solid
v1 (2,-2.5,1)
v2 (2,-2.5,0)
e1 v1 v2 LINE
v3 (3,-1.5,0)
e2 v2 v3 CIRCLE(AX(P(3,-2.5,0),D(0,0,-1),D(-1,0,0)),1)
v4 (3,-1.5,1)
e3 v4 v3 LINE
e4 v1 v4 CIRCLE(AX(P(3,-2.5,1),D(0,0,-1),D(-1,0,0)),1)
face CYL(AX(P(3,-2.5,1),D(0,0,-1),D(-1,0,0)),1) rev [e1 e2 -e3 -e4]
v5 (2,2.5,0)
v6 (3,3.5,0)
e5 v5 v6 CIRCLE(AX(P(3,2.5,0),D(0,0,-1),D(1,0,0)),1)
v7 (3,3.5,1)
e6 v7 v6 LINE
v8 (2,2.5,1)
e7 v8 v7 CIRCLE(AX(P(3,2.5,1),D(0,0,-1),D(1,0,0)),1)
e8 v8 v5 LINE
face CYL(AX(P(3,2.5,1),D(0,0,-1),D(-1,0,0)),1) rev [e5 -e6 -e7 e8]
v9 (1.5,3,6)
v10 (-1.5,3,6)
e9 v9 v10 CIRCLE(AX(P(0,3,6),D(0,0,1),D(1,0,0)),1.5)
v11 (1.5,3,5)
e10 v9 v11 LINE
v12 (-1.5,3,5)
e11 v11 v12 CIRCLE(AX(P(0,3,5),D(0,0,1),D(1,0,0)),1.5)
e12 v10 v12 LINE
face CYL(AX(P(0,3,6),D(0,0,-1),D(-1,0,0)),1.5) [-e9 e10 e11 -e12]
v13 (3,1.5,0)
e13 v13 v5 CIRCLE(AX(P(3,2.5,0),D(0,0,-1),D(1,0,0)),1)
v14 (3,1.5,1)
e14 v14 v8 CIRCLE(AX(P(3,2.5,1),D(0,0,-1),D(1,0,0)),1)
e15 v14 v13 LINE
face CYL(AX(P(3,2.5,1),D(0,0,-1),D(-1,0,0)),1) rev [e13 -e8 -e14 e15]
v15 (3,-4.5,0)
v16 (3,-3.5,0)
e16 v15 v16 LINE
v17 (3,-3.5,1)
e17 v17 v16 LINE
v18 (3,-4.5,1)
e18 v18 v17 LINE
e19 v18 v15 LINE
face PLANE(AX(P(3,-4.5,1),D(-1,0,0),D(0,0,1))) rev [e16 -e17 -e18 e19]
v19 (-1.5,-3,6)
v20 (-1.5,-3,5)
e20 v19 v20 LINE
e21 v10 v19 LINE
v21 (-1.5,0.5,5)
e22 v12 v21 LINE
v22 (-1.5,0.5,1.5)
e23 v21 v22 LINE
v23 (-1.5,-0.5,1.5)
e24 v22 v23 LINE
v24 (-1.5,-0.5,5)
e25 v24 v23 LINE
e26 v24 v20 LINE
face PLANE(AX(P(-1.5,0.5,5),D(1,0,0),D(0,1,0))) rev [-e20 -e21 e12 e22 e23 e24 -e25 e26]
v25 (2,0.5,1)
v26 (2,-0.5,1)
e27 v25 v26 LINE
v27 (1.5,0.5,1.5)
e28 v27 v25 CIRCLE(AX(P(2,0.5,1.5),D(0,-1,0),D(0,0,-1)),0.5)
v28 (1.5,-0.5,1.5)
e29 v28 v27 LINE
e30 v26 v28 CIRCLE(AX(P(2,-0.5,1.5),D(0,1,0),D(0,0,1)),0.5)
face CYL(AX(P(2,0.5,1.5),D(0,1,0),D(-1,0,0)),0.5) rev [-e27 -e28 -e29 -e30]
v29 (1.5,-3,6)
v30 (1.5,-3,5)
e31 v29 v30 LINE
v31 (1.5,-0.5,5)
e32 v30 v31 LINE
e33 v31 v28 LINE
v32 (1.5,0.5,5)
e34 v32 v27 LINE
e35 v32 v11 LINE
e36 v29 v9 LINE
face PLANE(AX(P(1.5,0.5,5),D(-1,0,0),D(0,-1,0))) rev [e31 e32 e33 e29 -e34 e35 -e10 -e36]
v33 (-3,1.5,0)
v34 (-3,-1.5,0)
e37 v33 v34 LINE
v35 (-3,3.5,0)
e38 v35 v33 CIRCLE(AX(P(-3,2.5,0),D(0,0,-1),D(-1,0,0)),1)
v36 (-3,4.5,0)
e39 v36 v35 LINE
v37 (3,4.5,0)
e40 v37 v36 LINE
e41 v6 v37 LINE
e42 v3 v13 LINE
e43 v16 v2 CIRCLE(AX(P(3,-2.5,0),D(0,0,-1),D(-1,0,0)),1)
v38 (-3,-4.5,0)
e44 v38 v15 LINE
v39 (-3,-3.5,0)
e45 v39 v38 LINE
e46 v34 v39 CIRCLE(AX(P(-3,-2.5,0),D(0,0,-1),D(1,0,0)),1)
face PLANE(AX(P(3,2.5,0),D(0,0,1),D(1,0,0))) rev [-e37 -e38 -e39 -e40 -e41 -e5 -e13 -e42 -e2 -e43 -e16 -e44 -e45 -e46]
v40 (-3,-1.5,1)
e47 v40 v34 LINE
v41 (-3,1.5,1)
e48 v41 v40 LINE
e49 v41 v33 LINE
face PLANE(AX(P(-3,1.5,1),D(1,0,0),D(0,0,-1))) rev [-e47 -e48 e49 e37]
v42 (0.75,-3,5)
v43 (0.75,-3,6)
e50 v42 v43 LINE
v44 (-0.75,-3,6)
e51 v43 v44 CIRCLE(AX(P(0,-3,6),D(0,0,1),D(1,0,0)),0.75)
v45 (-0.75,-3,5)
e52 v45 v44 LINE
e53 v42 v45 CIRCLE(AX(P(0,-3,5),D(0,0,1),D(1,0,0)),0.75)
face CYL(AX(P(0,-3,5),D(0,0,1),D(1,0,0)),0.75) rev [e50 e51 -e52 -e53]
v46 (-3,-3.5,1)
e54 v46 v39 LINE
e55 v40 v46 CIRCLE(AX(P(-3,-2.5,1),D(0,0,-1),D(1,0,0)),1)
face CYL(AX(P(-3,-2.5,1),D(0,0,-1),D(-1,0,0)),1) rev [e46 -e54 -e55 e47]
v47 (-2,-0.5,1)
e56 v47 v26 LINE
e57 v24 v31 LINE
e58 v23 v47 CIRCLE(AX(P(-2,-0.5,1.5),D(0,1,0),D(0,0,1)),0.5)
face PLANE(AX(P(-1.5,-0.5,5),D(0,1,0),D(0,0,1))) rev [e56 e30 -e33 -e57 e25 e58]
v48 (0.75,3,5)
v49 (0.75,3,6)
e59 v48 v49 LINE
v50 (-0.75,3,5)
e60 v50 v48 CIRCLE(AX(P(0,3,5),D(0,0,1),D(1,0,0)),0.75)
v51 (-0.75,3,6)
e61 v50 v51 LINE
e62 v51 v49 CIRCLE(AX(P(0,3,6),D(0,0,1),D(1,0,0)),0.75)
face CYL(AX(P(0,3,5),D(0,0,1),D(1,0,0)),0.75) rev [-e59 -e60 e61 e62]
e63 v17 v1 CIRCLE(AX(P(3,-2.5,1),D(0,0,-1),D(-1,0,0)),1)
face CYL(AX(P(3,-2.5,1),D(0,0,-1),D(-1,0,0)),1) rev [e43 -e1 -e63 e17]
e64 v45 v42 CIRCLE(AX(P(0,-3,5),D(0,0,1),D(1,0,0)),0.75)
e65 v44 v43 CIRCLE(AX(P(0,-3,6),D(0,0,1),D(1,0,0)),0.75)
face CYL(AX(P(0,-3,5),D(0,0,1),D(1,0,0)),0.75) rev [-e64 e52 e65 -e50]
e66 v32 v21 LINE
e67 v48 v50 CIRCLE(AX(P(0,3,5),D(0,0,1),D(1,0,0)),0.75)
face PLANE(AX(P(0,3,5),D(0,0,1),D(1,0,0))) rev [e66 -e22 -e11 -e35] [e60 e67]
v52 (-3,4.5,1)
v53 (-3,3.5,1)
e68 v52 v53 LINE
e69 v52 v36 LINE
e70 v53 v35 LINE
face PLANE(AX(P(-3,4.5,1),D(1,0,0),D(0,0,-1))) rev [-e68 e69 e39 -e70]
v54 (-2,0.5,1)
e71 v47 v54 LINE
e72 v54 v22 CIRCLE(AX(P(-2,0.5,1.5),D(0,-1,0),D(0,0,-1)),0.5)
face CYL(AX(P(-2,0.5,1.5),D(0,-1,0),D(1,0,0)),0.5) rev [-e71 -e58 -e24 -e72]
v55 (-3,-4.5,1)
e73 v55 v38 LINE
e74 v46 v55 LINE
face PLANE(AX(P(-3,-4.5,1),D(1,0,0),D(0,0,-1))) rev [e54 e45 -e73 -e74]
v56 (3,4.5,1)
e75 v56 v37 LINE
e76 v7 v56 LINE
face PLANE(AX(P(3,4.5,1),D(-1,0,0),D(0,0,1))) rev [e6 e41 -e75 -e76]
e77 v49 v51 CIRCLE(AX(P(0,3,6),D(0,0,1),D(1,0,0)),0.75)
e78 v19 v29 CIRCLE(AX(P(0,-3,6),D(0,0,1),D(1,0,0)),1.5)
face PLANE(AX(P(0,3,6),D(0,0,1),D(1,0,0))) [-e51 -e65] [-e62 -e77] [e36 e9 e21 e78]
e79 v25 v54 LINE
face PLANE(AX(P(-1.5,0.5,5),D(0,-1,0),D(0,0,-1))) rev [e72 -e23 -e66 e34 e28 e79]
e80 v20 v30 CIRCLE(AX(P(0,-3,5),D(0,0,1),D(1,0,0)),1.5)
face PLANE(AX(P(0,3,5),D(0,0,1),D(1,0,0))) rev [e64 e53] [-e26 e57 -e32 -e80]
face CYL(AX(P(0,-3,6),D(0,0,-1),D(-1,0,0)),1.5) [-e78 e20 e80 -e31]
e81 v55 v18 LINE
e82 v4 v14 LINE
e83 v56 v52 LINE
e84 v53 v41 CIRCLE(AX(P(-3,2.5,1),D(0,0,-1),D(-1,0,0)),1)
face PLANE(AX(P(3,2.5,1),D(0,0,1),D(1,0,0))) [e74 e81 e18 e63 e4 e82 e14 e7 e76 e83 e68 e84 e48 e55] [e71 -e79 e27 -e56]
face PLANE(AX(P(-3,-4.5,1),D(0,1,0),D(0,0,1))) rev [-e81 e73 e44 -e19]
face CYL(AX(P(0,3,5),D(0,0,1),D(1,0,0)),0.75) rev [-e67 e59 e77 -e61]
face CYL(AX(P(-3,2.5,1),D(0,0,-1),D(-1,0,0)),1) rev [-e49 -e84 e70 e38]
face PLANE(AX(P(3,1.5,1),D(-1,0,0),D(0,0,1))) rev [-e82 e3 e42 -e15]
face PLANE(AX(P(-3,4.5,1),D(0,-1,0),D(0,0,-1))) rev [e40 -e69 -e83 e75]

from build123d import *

# Parameters (mm, degrees)
BASE_PLATE_DEPTH   = 1
WEB_SKETCH_W       = 3
WEB_SKETCH_H       = 1
WEB_DEPTH          = 4
LUG_DEPTH          = 1
LUG_HOLES_SKETCH_R = 0.75
LUG_HOLES_2X_DEPTH = 1
WEB_FILLET_R0_5_R  = 0.5


with BuildPart() as part:
    # Base Plate Sketch → Base Plate (new body)
    with BuildSketch(Plane.XY):
        with BuildLine():
            Line((-3, 4.5), (3, 4.5))
            Line((3, 4.5), (3, 3.5))
            ThreePointArc((3, 3.5), (2, 2.5), (3, 1.5))
            Line((3, 1.5), (3, -1.5))
            ThreePointArc((3, -1.5), (2, -2.5), (3, -3.5))
            Line((3, -3.5), (3, -4.5))
            Line((3, -4.5), (-3, -4.5))
            Line((-3, -4.5), (-3, -3.5))
            ThreePointArc((-3, -3.5), (-2, -2.5), (-3, -1.5))
            Line((-3, -1.5), (-3, 1.5))
            ThreePointArc((-3, 1.5), (-2, 2.5), (-3, 3.5))
            Line((-3, 3.5), (-3, 4.5))
        make_face()
    extrude(amount=BASE_PLATE_DEPTH)

    # Web Sketch → Web (add)
    with BuildSketch(Plane.XY.offset(1)):
        Rectangle(WEB_SKETCH_W, WEB_SKETCH_H)
    extrude(amount=WEB_DEPTH)

    # Lug Sketch → Lug (add)
    with BuildSketch(Plane.XY.offset(5)):
        with BuildLine():
            Line((1.5, 3), (1.5, -3))
            ThreePointArc((1.5, -3), (0, -4.5), (-1.5, -3))
            Line((-1.5, -3), (-1.5, 3))
            ThreePointArc((-1.5, 3), (0, 4.5), (1.5, 3))
        make_face()
    extrude(amount=LUG_DEPTH)

    # Lug Holes Sketch → Lug Holes 2x (cut)
    with BuildSketch(Plane.XY.offset(6)):
        with Locations((0, 3)):
            Circle(LUG_HOLES_SKETCH_R)
        with Locations((0, -3)):
            Circle(LUG_HOLES_SKETCH_R)
    extrude(amount=-LUG_HOLES_2X_DEPTH, mode=Mode.SUBTRACT)

    # Web Fillet R0.5
    web_fillet_r0_5_edges = [part.edges().sort_by_distance(p)[0] for p in [
        (1.5, 0, 1),
        (-1.5, 0, 1),
    ]]
    fillet(web_fillet_r0_5_edges, radius=WEB_FILLET_R0_5_R)


solid = part.part
